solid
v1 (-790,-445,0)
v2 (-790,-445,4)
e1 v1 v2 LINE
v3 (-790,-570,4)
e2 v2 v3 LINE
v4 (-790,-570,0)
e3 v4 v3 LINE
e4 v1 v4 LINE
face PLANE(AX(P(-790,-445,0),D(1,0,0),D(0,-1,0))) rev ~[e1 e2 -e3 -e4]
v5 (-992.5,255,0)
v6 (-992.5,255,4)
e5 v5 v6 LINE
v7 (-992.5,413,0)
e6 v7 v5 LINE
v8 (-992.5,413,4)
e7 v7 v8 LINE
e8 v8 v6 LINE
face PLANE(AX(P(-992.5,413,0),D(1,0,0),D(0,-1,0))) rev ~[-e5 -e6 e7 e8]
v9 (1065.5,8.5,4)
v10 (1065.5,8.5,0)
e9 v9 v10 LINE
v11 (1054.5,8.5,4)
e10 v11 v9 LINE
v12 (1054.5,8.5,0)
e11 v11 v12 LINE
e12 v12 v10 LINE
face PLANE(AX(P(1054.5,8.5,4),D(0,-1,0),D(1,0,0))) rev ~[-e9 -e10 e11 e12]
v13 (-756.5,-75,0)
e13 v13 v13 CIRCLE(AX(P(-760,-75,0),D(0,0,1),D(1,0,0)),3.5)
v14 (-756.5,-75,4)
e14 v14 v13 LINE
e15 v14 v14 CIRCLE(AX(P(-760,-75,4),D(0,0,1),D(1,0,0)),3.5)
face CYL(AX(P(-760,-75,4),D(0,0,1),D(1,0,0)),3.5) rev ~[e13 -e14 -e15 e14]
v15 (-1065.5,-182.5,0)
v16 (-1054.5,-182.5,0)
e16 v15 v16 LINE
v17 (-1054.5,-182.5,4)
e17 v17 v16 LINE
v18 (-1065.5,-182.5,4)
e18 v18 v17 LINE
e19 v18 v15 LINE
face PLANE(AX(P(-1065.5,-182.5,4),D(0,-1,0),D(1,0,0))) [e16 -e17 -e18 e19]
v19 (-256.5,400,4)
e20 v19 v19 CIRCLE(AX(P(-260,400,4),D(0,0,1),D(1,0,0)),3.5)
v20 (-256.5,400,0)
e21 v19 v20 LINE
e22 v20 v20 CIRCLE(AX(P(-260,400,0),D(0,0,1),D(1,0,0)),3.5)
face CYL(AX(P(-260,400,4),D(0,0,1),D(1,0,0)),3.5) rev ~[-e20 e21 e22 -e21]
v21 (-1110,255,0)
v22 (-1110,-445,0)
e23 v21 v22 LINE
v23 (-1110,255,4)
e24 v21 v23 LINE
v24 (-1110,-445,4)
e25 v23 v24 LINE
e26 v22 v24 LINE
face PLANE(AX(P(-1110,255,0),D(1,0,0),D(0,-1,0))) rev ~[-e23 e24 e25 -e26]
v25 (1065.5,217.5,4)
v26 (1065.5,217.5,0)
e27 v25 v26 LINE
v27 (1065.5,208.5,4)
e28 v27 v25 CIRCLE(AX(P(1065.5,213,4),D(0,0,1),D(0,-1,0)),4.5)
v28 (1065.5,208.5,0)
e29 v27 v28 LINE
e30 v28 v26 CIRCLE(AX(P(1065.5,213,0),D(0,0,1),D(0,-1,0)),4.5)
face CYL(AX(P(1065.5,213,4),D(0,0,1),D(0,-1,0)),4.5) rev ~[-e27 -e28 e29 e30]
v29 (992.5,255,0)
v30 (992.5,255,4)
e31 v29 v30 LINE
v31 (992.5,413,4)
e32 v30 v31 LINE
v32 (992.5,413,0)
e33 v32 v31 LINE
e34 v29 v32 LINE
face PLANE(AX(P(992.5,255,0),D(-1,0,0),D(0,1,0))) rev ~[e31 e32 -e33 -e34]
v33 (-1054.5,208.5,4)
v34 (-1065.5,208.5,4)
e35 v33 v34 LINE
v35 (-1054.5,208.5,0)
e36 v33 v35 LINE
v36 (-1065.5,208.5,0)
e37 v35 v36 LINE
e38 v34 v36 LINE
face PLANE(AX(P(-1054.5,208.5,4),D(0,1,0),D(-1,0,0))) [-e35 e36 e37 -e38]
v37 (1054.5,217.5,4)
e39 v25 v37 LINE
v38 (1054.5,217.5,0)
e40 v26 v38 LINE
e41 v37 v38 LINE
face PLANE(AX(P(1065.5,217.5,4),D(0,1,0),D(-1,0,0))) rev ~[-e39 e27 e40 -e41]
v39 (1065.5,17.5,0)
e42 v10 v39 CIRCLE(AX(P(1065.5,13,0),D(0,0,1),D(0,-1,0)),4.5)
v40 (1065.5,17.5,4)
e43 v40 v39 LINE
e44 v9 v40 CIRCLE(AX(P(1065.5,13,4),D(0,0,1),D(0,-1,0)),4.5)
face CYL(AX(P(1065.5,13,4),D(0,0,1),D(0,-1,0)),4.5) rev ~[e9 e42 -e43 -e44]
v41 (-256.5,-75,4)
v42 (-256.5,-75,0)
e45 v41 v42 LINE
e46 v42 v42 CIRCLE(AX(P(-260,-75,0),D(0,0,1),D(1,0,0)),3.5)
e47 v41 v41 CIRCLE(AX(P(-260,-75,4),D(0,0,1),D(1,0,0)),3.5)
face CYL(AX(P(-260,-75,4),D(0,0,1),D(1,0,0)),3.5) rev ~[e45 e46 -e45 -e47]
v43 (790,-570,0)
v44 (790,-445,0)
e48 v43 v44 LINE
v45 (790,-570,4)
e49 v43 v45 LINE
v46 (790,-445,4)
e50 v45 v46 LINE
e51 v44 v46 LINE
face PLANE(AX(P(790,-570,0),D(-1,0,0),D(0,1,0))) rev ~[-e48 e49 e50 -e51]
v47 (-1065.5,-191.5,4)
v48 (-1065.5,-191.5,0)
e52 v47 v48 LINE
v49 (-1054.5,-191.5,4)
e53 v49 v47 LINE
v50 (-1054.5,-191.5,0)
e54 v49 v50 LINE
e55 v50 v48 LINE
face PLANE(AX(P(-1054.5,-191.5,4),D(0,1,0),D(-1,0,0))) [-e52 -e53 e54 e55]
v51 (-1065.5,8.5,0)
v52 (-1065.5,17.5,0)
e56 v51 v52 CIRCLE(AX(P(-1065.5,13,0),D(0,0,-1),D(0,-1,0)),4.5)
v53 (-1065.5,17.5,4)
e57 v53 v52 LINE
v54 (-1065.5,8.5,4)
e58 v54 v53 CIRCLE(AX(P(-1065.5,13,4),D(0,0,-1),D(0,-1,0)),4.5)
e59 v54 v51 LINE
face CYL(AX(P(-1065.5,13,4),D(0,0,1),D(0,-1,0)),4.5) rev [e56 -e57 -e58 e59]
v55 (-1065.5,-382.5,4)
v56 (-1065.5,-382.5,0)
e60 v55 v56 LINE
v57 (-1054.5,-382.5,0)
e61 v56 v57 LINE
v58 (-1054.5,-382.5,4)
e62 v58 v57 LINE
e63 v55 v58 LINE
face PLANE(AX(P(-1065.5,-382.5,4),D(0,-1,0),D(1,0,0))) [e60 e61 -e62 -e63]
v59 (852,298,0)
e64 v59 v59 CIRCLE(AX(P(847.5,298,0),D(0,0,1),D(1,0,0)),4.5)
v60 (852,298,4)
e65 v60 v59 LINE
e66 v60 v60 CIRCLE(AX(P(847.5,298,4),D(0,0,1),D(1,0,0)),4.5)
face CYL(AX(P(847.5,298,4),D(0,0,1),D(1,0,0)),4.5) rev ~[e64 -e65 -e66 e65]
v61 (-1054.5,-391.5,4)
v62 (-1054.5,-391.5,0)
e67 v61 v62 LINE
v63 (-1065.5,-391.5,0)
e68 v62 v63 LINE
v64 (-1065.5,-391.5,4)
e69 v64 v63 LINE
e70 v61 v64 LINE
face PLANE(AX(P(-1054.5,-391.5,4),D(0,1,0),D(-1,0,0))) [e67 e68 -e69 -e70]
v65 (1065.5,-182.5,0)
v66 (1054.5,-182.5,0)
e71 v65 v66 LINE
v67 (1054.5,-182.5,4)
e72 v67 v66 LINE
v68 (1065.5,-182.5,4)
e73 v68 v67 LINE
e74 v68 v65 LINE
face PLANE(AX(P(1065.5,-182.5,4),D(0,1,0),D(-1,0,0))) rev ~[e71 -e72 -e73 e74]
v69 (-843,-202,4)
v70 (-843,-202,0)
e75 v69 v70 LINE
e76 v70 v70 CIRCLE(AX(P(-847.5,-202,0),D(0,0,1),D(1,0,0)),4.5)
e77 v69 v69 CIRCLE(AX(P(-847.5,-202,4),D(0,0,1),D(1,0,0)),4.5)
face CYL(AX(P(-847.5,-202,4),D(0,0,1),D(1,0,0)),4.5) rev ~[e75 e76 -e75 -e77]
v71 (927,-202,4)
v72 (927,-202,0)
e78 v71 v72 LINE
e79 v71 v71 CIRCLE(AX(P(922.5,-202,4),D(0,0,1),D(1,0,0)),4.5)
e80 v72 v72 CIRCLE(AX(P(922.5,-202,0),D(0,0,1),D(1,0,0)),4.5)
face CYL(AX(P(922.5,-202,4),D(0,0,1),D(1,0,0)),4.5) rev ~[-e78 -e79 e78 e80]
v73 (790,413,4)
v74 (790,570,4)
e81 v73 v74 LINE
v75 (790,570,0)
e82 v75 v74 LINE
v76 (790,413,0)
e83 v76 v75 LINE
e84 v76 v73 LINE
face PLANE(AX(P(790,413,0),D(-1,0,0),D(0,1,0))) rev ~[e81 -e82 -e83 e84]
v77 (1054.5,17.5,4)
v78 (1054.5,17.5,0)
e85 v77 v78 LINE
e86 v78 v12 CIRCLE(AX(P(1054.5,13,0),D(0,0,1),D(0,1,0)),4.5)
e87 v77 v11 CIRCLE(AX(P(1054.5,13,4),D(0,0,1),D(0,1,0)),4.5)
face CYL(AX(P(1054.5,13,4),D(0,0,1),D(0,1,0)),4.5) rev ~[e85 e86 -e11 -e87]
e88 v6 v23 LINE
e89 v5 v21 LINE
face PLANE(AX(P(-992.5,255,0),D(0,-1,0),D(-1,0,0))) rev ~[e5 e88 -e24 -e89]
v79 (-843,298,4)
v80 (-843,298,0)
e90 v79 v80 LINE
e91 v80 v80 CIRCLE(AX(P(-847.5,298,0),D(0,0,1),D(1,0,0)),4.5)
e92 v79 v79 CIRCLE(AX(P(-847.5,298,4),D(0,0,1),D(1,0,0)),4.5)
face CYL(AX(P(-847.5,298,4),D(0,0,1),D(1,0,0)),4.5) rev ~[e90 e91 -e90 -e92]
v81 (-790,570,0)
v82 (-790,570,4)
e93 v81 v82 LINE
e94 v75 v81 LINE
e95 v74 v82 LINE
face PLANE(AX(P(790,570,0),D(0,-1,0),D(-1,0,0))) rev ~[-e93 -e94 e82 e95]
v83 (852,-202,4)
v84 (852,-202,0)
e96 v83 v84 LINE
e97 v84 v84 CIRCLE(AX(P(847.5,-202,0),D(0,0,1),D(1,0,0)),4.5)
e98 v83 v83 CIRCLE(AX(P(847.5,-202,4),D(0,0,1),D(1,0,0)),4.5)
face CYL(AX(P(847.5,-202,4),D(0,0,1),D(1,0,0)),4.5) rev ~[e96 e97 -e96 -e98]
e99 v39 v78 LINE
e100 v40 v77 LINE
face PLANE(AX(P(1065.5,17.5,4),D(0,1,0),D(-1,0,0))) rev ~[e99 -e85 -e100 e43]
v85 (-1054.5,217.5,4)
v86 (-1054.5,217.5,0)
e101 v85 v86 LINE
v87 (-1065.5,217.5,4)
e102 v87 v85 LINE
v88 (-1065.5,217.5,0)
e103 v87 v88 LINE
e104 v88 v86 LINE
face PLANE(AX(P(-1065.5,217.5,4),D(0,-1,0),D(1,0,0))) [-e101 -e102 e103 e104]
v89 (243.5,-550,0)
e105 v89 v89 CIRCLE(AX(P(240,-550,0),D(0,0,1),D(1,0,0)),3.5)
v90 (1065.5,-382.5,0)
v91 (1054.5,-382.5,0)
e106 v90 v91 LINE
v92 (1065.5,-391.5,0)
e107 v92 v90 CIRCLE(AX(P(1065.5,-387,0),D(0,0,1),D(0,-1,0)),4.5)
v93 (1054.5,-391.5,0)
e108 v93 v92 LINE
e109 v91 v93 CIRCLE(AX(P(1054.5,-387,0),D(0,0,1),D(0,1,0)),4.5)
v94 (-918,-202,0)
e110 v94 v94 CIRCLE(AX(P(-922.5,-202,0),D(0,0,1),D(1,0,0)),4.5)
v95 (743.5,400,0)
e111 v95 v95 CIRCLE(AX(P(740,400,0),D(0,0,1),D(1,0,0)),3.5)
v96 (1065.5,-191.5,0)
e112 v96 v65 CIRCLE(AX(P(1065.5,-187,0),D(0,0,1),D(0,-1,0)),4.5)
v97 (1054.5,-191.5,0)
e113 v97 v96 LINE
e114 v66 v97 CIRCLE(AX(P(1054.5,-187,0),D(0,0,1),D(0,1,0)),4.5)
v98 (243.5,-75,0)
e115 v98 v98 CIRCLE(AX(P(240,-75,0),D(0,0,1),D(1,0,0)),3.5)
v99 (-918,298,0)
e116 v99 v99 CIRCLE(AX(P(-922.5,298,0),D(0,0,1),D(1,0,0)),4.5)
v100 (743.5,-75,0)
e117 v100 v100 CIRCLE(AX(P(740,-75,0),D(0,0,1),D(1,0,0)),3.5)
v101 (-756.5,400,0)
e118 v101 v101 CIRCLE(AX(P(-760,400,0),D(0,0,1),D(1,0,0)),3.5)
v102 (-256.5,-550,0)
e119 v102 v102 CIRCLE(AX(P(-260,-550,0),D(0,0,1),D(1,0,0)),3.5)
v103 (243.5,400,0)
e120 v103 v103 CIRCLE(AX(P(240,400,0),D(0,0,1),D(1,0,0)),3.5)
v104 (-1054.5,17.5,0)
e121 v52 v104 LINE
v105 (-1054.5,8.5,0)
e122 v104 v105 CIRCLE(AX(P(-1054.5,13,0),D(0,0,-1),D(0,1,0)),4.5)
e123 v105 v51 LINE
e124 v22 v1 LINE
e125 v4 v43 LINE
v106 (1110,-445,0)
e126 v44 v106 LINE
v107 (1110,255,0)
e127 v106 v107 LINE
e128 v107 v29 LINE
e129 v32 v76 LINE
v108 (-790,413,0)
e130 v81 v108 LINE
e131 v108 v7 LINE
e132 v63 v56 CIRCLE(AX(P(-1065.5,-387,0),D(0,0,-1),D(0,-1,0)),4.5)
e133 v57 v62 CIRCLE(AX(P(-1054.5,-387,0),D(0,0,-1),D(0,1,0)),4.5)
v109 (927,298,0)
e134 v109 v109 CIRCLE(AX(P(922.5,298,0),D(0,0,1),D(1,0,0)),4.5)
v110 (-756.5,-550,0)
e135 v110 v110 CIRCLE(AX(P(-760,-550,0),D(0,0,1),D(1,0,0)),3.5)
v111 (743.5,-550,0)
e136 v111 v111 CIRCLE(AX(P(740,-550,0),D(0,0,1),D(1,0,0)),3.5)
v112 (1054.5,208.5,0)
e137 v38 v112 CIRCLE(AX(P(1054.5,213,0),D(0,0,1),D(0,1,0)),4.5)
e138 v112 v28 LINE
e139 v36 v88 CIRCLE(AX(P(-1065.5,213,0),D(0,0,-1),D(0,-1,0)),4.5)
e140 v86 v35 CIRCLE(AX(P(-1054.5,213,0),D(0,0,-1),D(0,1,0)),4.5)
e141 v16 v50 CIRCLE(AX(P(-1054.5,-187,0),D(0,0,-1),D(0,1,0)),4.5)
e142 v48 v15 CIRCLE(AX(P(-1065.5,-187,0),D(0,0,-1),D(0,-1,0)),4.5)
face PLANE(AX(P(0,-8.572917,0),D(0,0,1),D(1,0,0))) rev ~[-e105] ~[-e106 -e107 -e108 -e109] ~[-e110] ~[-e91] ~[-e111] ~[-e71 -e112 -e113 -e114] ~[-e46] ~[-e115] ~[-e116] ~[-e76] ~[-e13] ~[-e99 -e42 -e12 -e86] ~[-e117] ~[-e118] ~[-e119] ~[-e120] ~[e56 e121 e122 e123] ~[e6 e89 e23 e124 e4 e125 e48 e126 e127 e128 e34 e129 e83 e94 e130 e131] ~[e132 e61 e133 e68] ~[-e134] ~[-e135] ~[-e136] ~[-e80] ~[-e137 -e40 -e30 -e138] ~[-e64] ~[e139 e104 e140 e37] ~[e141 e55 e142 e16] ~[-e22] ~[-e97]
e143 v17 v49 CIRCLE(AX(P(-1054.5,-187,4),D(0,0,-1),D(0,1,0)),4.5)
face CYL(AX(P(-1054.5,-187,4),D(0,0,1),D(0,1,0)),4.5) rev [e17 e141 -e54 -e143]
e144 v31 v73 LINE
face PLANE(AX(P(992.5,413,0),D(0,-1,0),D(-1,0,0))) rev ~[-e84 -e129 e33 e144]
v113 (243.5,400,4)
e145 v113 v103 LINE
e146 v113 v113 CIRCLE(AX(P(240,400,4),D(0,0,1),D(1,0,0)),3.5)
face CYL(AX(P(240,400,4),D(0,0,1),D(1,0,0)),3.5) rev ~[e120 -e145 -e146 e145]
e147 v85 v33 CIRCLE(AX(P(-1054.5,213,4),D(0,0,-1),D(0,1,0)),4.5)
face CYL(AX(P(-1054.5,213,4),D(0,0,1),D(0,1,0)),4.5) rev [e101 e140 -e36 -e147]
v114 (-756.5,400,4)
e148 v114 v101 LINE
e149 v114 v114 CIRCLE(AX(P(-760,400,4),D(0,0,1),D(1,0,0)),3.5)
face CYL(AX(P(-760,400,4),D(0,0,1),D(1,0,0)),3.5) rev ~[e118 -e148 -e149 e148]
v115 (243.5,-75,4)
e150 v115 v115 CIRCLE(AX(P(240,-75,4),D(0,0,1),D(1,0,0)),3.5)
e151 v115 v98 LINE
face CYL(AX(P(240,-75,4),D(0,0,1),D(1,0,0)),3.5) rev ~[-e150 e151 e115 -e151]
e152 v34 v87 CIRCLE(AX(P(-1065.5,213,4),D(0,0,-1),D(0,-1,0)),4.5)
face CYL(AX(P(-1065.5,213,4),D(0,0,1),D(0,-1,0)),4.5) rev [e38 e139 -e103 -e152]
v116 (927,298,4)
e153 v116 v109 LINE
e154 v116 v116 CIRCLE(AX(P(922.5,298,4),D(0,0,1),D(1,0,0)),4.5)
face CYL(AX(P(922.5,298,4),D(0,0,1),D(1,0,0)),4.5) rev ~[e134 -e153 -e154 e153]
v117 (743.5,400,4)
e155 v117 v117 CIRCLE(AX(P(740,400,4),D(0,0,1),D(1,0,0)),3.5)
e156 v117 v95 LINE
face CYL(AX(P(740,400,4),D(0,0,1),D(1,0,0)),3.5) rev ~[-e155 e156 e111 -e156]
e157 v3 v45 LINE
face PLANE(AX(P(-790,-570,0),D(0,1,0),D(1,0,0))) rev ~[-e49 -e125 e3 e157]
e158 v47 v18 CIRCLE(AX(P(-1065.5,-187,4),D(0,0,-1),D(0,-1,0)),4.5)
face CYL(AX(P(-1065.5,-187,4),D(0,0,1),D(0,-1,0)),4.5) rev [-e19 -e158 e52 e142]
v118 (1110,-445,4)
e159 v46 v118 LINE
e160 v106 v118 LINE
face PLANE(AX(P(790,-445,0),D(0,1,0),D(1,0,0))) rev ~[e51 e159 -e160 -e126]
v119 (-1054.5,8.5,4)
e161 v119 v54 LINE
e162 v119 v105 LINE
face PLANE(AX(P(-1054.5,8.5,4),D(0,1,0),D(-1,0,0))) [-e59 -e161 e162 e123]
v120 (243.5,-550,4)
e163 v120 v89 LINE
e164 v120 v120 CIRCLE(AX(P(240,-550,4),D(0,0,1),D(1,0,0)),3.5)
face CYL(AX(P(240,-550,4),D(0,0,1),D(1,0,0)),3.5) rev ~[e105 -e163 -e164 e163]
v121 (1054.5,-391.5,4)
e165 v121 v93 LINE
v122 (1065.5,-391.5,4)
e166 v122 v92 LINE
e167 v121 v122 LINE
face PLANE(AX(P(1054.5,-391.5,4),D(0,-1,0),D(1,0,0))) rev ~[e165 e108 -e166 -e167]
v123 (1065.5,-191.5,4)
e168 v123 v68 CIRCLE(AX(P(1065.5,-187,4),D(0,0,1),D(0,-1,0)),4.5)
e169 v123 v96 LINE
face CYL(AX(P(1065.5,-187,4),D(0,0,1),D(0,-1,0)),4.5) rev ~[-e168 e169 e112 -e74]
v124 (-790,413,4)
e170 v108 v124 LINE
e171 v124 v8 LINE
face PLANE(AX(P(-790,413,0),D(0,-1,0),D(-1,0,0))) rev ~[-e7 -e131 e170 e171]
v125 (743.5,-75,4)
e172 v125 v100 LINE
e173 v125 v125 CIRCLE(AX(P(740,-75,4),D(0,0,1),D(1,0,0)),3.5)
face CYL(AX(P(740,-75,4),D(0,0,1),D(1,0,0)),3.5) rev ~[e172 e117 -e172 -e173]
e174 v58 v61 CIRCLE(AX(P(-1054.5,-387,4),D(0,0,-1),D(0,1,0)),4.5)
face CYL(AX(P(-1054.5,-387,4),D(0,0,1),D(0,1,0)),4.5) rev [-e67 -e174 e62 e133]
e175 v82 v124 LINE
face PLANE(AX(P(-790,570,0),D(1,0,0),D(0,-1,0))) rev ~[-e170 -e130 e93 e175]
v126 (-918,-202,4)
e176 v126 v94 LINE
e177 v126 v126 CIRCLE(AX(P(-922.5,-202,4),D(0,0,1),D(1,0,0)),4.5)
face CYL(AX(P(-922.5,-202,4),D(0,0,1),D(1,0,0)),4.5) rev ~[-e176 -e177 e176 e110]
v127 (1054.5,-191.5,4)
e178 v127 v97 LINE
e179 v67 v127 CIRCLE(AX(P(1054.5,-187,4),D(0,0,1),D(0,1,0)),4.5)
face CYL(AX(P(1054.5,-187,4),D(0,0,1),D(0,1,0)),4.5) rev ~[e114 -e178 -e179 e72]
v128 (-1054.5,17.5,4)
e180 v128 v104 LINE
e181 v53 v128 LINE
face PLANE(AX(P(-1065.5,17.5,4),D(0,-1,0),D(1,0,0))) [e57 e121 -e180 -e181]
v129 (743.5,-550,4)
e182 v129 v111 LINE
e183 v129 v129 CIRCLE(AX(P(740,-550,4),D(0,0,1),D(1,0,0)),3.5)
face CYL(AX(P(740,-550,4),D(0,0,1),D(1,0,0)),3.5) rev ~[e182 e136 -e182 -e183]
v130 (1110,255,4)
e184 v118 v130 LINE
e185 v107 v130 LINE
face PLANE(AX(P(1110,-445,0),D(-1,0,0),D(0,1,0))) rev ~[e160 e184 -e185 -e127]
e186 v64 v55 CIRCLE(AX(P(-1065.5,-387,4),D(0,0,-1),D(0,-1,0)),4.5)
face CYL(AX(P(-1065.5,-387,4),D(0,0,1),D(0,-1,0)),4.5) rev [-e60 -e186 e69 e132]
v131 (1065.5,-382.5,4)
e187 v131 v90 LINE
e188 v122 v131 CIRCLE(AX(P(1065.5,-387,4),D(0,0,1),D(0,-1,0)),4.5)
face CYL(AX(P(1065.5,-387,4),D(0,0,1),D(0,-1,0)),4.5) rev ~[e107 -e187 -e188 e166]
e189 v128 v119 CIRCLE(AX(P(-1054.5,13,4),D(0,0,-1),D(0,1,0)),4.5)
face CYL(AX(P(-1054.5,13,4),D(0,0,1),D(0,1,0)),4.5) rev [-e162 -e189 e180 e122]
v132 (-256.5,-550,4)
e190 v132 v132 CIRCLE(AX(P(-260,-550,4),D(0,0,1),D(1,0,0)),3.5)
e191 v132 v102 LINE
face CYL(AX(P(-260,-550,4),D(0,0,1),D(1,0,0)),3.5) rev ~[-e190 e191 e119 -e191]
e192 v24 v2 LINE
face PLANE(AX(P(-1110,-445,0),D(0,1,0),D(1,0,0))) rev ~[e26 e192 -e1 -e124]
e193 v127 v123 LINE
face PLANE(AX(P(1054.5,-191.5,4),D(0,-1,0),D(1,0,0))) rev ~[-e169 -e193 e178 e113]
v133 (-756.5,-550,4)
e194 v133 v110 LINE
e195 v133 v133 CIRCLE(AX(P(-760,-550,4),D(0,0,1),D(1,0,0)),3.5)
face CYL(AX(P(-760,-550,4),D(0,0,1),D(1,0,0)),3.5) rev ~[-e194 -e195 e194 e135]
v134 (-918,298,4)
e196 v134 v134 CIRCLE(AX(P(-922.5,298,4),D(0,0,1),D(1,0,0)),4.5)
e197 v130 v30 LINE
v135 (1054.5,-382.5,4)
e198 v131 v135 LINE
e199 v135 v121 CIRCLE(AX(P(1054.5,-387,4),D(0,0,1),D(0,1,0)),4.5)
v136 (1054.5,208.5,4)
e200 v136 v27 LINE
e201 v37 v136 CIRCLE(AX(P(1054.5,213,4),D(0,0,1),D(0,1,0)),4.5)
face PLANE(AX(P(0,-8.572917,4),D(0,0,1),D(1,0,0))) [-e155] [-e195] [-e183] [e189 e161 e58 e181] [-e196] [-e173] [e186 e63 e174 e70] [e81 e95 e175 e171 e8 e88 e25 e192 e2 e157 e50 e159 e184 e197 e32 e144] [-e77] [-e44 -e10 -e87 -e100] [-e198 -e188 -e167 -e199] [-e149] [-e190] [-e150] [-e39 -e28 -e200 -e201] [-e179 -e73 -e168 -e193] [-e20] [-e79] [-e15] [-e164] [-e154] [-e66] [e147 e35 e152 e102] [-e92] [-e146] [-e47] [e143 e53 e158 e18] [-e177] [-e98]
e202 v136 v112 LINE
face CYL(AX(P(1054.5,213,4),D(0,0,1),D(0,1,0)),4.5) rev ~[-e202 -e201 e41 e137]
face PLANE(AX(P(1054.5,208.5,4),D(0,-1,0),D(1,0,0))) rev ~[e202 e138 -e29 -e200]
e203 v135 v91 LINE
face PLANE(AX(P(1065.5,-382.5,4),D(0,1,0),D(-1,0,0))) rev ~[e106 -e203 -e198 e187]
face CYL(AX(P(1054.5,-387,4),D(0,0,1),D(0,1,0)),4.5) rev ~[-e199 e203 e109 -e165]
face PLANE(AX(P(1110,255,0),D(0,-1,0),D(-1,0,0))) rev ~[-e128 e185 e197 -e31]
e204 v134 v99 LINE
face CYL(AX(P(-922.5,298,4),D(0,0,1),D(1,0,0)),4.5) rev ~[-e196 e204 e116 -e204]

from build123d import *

# Parameters (mm, degrees)
BOSS_EXTRUDE1_DEPTH = 4
SKETCH2_R           = 3.5
SKETCH2_R_2         = 4.5
CUT_EXTRUDE1_DEPTH  = 4


with BuildPart() as part:
    # Sketch1 → Boss-Extrude1 (new body)
    with BuildSketch(Plane.XY):
        Polygon((-790, 570), (-790, 413), (-992.5, 413), (-992.5, 255), (-1110, 255), (-1110, -445), (-790, -445), (-790, -570), (790, -570), (790, -445), (1110, -445), (1110, 255), (992.5, 255), (992.5, 413), (790, 413), (790, 570), align=None)
    extrude(amount=BOSS_EXTRUDE1_DEPTH)

    # Sketch2 → Cut-Extrude1 (cut)
    with BuildSketch(Plane.XY.offset(4)):
        with Locations((-760, 400)):
            Circle(SKETCH2_R)
        with Locations((-260, 400)):
            Circle(SKETCH2_R)
        with Locations((240, 400)):
            Circle(SKETCH2_R)
        with Locations((740, 400)):
            Circle(SKETCH2_R)
        with Locations((-760, -75)):
            Circle(SKETCH2_R)
        with Locations((-260, -75)):
            Circle(SKETCH2_R)
        with Locations((240, -75)):
            Circle(SKETCH2_R)
        with Locations((740, -75)):
            Circle(SKETCH2_R)
        with Locations((-760, -550)):
            Circle(SKETCH2_R)
        with Locations((-260, -550)):
            Circle(SKETCH2_R)
        with Locations((240, -550)):
            Circle(SKETCH2_R)
        with Locations((740, -550)):
            Circle(SKETCH2_R)
        with Locations((-922.5, 298)):
            Circle(SKETCH2_R_2)
        with Locations((-847.5, 298)):
            Circle(SKETCH2_R_2)
        with Locations((-922.5, -202)):
            Circle(SKETCH2_R_2)
        with Locations((-847.5, -202)):
            Circle(SKETCH2_R_2)
        with Locations((847.5, 298)):
            Circle(SKETCH2_R_2)
        with Locations((922.5, 298)):
            Circle(SKETCH2_R_2)
        with Locations((847.5, -202)):
            Circle(SKETCH2_R_2)
        with Locations((922.5, -202)):
            Circle(SKETCH2_R_2)
        with BuildLine():
            Line((-1065.5, 217.5), (-1054.5, 217.5))
            ThreePointArc((-1054.5, 217.5), (-1050, 213), (-1054.5, 208.5))
            Line((-1054.5, 208.5), (-1065.5, 208.5))
            ThreePointArc((-1065.5, 208.5), (-1070, 213), (-1065.5, 217.5))
        make_face()
        with BuildLine():
            Line((-1065.5, 17.5), (-1054.5, 17.5))
            ThreePointArc((-1054.5, 17.5), (-1050, 13), (-1054.5, 8.5))
            Line((-1054.5, 8.5), (-1065.5, 8.5))
            ThreePointArc((-1065.5, 8.5), (-1070, 13), (-1065.5, 17.5))
        make_face()
        with BuildLine():
            Line((-1065.5, -182.5), (-1054.5, -182.5))
            ThreePointArc((-1054.5, -182.5), (-1050, -187), (-1054.5, -191.5))
            Line((-1054.5, -191.5), (-1065.5, -191.5))
            ThreePointArc((-1065.5, -191.5), (-1070, -187), (-1065.5, -182.5))
        make_face()
        with BuildLine():
            Line((-1065.5, -382.5), (-1054.5, -382.5))
            ThreePointArc((-1054.5, -382.5), (-1050, -387), (-1054.5, -391.5))
            Line((-1054.5, -391.5), (-1065.5, -391.5))
            ThreePointArc((-1065.5, -391.5), (-1070, -387), (-1065.5, -382.5))
        make_face()
        with BuildLine():
            Line((1065.5, -382.5), (1054.5, -382.5))
            ThreePointArc((1054.5, -382.5), (1050, -387), (1054.5, -391.5))
            Line((1054.5, -391.5), (1065.5, -391.5))
            ThreePointArc((1065.5, -391.5), (1070, -387), (1065.5, -382.5))
        make_face()
        with BuildLine():
            Line((1065.5, -182.5), (1054.5, -182.5))
            ThreePointArc((1054.5, -182.5), (1050, -187), (1054.5, -191.5))
            Line((1054.5, -191.5), (1065.5, -191.5))
            ThreePointArc((1065.5, -191.5), (1070, -187), (1065.5, -182.5))
        make_face()
        with BuildLine():
            Line((1065.5, 17.5), (1054.5, 17.5))
            ThreePointArc((1054.5, 17.5), (1050, 13), (1054.5, 8.5))
            Line((1054.5, 8.5), (1065.5, 8.5))
            ThreePointArc((1065.5, 8.5), (1070, 13), (1065.5, 17.5))
        make_face()
        with BuildLine():
            Line((1065.5, 217.5), (1054.5, 217.5))
            ThreePointArc((1054.5, 217.5), (1050, 213), (1054.5, 208.5))
            Line((1054.5, 208.5), (1065.5, 208.5))
            ThreePointArc((1065.5, 208.5), (1070, 213), (1065.5, 217.5))
        make_face()
    extrude(amount=-CUT_EXTRUDE1_DEPTH, mode=Mode.SUBTRACT)


solid = part.part
